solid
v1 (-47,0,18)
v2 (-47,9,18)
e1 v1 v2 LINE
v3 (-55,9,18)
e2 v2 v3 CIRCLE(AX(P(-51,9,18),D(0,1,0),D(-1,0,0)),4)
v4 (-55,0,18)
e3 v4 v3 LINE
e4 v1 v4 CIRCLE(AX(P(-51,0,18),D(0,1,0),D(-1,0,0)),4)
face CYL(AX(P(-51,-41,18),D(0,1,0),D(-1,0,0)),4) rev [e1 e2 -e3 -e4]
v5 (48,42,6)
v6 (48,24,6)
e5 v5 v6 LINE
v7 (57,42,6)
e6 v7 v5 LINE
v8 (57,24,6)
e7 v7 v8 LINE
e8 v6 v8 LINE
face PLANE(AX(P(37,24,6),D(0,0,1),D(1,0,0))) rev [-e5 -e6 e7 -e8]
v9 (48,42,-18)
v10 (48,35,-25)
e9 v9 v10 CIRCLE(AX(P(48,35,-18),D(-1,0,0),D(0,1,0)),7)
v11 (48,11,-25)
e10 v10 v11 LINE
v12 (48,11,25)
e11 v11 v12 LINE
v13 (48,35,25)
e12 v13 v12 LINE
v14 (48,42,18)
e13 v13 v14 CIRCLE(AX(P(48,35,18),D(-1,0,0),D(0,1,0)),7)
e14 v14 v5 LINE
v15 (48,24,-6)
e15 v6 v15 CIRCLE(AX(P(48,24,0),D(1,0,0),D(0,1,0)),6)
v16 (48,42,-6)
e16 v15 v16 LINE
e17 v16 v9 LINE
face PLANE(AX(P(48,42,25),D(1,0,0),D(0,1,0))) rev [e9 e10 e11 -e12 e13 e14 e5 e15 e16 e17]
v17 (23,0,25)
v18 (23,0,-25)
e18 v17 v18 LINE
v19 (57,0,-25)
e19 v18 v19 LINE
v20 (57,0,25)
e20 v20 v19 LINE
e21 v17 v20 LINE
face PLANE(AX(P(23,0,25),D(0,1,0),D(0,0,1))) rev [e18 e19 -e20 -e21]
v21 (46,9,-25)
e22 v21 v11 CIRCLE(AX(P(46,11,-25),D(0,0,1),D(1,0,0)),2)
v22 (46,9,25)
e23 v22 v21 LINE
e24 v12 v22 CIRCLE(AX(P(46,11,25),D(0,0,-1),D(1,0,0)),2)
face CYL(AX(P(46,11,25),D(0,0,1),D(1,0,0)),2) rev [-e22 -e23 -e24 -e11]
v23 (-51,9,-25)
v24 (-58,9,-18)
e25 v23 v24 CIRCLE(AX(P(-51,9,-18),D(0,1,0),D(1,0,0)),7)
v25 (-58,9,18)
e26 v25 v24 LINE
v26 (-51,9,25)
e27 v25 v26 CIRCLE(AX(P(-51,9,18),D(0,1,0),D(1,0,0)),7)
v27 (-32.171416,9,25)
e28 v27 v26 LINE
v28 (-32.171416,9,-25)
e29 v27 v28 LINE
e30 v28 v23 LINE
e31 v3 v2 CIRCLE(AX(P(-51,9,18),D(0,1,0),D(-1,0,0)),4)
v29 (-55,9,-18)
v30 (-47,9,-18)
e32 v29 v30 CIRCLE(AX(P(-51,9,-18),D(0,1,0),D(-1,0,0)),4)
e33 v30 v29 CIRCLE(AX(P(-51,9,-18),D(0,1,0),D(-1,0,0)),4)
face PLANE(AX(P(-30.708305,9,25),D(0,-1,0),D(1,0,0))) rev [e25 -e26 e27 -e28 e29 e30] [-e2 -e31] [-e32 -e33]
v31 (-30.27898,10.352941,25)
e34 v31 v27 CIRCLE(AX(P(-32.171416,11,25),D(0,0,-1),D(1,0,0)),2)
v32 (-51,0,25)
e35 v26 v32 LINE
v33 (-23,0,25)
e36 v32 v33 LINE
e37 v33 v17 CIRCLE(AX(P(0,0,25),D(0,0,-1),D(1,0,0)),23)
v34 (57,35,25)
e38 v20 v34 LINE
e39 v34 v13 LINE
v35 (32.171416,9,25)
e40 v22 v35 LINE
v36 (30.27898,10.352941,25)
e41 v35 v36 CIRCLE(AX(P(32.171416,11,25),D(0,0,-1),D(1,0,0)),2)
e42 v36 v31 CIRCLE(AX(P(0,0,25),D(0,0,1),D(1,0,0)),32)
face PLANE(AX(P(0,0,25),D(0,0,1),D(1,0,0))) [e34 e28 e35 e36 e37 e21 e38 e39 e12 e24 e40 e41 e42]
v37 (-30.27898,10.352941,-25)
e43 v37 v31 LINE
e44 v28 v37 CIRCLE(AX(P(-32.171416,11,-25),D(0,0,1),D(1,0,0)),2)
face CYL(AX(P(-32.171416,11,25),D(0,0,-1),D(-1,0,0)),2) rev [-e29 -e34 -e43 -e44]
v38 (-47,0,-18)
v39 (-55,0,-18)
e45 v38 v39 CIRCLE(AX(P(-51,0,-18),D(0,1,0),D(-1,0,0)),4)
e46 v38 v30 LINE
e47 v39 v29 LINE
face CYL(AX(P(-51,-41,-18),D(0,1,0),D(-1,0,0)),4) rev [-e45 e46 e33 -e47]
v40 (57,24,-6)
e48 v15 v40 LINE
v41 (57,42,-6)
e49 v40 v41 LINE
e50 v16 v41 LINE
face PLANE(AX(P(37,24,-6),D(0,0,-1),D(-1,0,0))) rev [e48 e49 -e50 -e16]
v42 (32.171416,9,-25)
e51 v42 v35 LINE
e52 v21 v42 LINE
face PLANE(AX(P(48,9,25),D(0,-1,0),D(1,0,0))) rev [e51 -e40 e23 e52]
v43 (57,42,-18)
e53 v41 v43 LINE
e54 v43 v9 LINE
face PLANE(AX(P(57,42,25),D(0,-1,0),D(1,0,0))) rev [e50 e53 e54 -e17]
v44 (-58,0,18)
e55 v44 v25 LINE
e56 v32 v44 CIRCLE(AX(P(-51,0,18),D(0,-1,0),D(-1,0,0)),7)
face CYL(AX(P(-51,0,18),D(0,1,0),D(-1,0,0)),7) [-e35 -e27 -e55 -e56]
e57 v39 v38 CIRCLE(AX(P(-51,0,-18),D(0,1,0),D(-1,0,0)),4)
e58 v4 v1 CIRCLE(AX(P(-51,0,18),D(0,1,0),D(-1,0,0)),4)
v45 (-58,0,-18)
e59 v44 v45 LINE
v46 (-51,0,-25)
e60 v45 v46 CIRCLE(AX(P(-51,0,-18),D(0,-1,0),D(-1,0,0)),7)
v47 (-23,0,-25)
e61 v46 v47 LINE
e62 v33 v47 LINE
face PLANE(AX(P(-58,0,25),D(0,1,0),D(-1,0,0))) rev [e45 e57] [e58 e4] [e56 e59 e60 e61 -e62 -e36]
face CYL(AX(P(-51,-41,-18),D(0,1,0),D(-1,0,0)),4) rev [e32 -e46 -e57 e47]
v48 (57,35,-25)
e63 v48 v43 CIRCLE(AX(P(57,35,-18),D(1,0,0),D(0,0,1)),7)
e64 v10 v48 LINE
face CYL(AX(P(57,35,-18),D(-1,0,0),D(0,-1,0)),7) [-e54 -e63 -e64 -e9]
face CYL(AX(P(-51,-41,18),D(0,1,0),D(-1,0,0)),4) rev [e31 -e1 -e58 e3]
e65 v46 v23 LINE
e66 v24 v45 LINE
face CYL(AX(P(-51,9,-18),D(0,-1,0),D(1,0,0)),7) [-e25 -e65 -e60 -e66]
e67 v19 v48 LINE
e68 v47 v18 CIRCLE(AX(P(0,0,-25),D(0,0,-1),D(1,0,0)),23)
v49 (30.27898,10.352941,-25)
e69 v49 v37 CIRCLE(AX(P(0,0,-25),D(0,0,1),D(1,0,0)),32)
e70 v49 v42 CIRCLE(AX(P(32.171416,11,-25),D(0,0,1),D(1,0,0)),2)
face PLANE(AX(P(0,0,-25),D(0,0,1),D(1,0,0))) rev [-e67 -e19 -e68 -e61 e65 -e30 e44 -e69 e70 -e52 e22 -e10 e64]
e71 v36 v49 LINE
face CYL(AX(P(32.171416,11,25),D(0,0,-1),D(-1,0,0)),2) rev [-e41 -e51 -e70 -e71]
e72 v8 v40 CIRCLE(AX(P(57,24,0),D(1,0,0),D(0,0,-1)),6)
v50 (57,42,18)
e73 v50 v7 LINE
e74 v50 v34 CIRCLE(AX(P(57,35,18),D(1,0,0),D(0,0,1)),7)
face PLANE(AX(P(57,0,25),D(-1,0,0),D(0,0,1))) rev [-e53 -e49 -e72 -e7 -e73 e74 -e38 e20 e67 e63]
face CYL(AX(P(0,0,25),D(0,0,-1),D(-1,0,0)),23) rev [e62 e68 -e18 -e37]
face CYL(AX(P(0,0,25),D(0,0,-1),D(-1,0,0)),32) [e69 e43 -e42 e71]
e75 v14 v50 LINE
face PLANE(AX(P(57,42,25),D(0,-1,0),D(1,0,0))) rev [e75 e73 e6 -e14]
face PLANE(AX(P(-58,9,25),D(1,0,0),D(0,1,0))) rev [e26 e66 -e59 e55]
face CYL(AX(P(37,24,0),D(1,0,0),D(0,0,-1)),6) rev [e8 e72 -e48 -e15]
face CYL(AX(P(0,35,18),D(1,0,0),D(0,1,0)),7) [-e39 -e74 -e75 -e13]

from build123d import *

# Parameters (mm, degrees)
SADDLE_BODY_DEPTH     = 25
EDGE_FILLETS_R2_R     = 2
CORNER_FILLETS_R7_R   = 7
FLANGE_HOLES_SKETCH_R = 4
FLANGE_HOLES_DEPTH    = 50
U_SLOT_CUT_DEPTH      = 20


with BuildPart() as part:
    # Saddle Profile Sketch → Saddle Body (new, symmetric)
    with BuildSketch(Plane.XY):
        with BuildLine():
            Line((-58, 0), (-23, 0))
            ThreePointArc((-23, 0), (0, 23), (23, 0))
            Line((23, 0), (57, 0))
            Line((57, 0), (57, 42))
            Line((57, 42), (48, 42))
            Line((48, 42), (48, 9))
            Line((48, 9), (30.708305066, 9))
            ThreePointArc((30.708305066, 9), (0, 32), (-30.708305066, 9))
            Line((-30.708305066, 9), (-58, 9))
            Line((-58, 9), (-58, 0))
        make_face()
    extrude(amount=SADDLE_BODY_DEPTH, both=True)

    # Edge Fillets R2
    edge_fillets_r2_edges = [part.edges().sort_by_distance(p)[0] for p in [
        (-30.708305066, 9, 0),
        (30.708305066, 9, 0),
        (48, 9, 0),
    ]]
    fillet(edge_fillets_r2_edges, radius=EDGE_FILLETS_R2_R)

    # Corner Fillets R7
    corner_fillets_r7_edges = [part.edges().sort_by_distance(p)[0] for p in [
        (-58, 4.5, -25),
        (52.5, 42, -25),
        (52.5, 42, 25),
        (-58, 4.5, 25),
    ]]
    fillet(corner_fillets_r7_edges, radius=CORNER_FILLETS_R7_R)

    # Flange Holes Sketch → Flange Holes (cut)
    with BuildSketch(Plane(origin=(0, 9, 0), x_dir=(1, 0, 0), z_dir=(0, 1, 0))):
        with Locations(Location((-51, 18, 0), (0, 0, 180))):
            Circle(FLANGE_HOLES_SKETCH_R)
        with Locations(Location((-51, -18, 0), (0, 0, 180))):
            Circle(FLANGE_HOLES_SKETCH_R)
    extrude(amount=-FLANGE_HOLES_DEPTH, mode=Mode.SUBTRACT)

    # U-Slot Sketch → U-Slot Cut (cut)
    with BuildSketch(Plane(origin=(57, 0, 0), x_dir=(0, 0, -1), z_dir=(1, 0, 0))):
        with BuildLine():
            Line((-6, 24), (-6, 44.935144294))
            ThreePointArc((-6, 44.935144294), (0, 50.935144294), (6, 44.935144294))
            Line((6, 44.935144294), (6, 24))
            ThreePointArc((6, 24), (0, 18), (-6, 24))
        make_face()
    extrude(amount=-U_SLOT_CUT_DEPTH, mode=Mode.SUBTRACT)


solid = part.part
